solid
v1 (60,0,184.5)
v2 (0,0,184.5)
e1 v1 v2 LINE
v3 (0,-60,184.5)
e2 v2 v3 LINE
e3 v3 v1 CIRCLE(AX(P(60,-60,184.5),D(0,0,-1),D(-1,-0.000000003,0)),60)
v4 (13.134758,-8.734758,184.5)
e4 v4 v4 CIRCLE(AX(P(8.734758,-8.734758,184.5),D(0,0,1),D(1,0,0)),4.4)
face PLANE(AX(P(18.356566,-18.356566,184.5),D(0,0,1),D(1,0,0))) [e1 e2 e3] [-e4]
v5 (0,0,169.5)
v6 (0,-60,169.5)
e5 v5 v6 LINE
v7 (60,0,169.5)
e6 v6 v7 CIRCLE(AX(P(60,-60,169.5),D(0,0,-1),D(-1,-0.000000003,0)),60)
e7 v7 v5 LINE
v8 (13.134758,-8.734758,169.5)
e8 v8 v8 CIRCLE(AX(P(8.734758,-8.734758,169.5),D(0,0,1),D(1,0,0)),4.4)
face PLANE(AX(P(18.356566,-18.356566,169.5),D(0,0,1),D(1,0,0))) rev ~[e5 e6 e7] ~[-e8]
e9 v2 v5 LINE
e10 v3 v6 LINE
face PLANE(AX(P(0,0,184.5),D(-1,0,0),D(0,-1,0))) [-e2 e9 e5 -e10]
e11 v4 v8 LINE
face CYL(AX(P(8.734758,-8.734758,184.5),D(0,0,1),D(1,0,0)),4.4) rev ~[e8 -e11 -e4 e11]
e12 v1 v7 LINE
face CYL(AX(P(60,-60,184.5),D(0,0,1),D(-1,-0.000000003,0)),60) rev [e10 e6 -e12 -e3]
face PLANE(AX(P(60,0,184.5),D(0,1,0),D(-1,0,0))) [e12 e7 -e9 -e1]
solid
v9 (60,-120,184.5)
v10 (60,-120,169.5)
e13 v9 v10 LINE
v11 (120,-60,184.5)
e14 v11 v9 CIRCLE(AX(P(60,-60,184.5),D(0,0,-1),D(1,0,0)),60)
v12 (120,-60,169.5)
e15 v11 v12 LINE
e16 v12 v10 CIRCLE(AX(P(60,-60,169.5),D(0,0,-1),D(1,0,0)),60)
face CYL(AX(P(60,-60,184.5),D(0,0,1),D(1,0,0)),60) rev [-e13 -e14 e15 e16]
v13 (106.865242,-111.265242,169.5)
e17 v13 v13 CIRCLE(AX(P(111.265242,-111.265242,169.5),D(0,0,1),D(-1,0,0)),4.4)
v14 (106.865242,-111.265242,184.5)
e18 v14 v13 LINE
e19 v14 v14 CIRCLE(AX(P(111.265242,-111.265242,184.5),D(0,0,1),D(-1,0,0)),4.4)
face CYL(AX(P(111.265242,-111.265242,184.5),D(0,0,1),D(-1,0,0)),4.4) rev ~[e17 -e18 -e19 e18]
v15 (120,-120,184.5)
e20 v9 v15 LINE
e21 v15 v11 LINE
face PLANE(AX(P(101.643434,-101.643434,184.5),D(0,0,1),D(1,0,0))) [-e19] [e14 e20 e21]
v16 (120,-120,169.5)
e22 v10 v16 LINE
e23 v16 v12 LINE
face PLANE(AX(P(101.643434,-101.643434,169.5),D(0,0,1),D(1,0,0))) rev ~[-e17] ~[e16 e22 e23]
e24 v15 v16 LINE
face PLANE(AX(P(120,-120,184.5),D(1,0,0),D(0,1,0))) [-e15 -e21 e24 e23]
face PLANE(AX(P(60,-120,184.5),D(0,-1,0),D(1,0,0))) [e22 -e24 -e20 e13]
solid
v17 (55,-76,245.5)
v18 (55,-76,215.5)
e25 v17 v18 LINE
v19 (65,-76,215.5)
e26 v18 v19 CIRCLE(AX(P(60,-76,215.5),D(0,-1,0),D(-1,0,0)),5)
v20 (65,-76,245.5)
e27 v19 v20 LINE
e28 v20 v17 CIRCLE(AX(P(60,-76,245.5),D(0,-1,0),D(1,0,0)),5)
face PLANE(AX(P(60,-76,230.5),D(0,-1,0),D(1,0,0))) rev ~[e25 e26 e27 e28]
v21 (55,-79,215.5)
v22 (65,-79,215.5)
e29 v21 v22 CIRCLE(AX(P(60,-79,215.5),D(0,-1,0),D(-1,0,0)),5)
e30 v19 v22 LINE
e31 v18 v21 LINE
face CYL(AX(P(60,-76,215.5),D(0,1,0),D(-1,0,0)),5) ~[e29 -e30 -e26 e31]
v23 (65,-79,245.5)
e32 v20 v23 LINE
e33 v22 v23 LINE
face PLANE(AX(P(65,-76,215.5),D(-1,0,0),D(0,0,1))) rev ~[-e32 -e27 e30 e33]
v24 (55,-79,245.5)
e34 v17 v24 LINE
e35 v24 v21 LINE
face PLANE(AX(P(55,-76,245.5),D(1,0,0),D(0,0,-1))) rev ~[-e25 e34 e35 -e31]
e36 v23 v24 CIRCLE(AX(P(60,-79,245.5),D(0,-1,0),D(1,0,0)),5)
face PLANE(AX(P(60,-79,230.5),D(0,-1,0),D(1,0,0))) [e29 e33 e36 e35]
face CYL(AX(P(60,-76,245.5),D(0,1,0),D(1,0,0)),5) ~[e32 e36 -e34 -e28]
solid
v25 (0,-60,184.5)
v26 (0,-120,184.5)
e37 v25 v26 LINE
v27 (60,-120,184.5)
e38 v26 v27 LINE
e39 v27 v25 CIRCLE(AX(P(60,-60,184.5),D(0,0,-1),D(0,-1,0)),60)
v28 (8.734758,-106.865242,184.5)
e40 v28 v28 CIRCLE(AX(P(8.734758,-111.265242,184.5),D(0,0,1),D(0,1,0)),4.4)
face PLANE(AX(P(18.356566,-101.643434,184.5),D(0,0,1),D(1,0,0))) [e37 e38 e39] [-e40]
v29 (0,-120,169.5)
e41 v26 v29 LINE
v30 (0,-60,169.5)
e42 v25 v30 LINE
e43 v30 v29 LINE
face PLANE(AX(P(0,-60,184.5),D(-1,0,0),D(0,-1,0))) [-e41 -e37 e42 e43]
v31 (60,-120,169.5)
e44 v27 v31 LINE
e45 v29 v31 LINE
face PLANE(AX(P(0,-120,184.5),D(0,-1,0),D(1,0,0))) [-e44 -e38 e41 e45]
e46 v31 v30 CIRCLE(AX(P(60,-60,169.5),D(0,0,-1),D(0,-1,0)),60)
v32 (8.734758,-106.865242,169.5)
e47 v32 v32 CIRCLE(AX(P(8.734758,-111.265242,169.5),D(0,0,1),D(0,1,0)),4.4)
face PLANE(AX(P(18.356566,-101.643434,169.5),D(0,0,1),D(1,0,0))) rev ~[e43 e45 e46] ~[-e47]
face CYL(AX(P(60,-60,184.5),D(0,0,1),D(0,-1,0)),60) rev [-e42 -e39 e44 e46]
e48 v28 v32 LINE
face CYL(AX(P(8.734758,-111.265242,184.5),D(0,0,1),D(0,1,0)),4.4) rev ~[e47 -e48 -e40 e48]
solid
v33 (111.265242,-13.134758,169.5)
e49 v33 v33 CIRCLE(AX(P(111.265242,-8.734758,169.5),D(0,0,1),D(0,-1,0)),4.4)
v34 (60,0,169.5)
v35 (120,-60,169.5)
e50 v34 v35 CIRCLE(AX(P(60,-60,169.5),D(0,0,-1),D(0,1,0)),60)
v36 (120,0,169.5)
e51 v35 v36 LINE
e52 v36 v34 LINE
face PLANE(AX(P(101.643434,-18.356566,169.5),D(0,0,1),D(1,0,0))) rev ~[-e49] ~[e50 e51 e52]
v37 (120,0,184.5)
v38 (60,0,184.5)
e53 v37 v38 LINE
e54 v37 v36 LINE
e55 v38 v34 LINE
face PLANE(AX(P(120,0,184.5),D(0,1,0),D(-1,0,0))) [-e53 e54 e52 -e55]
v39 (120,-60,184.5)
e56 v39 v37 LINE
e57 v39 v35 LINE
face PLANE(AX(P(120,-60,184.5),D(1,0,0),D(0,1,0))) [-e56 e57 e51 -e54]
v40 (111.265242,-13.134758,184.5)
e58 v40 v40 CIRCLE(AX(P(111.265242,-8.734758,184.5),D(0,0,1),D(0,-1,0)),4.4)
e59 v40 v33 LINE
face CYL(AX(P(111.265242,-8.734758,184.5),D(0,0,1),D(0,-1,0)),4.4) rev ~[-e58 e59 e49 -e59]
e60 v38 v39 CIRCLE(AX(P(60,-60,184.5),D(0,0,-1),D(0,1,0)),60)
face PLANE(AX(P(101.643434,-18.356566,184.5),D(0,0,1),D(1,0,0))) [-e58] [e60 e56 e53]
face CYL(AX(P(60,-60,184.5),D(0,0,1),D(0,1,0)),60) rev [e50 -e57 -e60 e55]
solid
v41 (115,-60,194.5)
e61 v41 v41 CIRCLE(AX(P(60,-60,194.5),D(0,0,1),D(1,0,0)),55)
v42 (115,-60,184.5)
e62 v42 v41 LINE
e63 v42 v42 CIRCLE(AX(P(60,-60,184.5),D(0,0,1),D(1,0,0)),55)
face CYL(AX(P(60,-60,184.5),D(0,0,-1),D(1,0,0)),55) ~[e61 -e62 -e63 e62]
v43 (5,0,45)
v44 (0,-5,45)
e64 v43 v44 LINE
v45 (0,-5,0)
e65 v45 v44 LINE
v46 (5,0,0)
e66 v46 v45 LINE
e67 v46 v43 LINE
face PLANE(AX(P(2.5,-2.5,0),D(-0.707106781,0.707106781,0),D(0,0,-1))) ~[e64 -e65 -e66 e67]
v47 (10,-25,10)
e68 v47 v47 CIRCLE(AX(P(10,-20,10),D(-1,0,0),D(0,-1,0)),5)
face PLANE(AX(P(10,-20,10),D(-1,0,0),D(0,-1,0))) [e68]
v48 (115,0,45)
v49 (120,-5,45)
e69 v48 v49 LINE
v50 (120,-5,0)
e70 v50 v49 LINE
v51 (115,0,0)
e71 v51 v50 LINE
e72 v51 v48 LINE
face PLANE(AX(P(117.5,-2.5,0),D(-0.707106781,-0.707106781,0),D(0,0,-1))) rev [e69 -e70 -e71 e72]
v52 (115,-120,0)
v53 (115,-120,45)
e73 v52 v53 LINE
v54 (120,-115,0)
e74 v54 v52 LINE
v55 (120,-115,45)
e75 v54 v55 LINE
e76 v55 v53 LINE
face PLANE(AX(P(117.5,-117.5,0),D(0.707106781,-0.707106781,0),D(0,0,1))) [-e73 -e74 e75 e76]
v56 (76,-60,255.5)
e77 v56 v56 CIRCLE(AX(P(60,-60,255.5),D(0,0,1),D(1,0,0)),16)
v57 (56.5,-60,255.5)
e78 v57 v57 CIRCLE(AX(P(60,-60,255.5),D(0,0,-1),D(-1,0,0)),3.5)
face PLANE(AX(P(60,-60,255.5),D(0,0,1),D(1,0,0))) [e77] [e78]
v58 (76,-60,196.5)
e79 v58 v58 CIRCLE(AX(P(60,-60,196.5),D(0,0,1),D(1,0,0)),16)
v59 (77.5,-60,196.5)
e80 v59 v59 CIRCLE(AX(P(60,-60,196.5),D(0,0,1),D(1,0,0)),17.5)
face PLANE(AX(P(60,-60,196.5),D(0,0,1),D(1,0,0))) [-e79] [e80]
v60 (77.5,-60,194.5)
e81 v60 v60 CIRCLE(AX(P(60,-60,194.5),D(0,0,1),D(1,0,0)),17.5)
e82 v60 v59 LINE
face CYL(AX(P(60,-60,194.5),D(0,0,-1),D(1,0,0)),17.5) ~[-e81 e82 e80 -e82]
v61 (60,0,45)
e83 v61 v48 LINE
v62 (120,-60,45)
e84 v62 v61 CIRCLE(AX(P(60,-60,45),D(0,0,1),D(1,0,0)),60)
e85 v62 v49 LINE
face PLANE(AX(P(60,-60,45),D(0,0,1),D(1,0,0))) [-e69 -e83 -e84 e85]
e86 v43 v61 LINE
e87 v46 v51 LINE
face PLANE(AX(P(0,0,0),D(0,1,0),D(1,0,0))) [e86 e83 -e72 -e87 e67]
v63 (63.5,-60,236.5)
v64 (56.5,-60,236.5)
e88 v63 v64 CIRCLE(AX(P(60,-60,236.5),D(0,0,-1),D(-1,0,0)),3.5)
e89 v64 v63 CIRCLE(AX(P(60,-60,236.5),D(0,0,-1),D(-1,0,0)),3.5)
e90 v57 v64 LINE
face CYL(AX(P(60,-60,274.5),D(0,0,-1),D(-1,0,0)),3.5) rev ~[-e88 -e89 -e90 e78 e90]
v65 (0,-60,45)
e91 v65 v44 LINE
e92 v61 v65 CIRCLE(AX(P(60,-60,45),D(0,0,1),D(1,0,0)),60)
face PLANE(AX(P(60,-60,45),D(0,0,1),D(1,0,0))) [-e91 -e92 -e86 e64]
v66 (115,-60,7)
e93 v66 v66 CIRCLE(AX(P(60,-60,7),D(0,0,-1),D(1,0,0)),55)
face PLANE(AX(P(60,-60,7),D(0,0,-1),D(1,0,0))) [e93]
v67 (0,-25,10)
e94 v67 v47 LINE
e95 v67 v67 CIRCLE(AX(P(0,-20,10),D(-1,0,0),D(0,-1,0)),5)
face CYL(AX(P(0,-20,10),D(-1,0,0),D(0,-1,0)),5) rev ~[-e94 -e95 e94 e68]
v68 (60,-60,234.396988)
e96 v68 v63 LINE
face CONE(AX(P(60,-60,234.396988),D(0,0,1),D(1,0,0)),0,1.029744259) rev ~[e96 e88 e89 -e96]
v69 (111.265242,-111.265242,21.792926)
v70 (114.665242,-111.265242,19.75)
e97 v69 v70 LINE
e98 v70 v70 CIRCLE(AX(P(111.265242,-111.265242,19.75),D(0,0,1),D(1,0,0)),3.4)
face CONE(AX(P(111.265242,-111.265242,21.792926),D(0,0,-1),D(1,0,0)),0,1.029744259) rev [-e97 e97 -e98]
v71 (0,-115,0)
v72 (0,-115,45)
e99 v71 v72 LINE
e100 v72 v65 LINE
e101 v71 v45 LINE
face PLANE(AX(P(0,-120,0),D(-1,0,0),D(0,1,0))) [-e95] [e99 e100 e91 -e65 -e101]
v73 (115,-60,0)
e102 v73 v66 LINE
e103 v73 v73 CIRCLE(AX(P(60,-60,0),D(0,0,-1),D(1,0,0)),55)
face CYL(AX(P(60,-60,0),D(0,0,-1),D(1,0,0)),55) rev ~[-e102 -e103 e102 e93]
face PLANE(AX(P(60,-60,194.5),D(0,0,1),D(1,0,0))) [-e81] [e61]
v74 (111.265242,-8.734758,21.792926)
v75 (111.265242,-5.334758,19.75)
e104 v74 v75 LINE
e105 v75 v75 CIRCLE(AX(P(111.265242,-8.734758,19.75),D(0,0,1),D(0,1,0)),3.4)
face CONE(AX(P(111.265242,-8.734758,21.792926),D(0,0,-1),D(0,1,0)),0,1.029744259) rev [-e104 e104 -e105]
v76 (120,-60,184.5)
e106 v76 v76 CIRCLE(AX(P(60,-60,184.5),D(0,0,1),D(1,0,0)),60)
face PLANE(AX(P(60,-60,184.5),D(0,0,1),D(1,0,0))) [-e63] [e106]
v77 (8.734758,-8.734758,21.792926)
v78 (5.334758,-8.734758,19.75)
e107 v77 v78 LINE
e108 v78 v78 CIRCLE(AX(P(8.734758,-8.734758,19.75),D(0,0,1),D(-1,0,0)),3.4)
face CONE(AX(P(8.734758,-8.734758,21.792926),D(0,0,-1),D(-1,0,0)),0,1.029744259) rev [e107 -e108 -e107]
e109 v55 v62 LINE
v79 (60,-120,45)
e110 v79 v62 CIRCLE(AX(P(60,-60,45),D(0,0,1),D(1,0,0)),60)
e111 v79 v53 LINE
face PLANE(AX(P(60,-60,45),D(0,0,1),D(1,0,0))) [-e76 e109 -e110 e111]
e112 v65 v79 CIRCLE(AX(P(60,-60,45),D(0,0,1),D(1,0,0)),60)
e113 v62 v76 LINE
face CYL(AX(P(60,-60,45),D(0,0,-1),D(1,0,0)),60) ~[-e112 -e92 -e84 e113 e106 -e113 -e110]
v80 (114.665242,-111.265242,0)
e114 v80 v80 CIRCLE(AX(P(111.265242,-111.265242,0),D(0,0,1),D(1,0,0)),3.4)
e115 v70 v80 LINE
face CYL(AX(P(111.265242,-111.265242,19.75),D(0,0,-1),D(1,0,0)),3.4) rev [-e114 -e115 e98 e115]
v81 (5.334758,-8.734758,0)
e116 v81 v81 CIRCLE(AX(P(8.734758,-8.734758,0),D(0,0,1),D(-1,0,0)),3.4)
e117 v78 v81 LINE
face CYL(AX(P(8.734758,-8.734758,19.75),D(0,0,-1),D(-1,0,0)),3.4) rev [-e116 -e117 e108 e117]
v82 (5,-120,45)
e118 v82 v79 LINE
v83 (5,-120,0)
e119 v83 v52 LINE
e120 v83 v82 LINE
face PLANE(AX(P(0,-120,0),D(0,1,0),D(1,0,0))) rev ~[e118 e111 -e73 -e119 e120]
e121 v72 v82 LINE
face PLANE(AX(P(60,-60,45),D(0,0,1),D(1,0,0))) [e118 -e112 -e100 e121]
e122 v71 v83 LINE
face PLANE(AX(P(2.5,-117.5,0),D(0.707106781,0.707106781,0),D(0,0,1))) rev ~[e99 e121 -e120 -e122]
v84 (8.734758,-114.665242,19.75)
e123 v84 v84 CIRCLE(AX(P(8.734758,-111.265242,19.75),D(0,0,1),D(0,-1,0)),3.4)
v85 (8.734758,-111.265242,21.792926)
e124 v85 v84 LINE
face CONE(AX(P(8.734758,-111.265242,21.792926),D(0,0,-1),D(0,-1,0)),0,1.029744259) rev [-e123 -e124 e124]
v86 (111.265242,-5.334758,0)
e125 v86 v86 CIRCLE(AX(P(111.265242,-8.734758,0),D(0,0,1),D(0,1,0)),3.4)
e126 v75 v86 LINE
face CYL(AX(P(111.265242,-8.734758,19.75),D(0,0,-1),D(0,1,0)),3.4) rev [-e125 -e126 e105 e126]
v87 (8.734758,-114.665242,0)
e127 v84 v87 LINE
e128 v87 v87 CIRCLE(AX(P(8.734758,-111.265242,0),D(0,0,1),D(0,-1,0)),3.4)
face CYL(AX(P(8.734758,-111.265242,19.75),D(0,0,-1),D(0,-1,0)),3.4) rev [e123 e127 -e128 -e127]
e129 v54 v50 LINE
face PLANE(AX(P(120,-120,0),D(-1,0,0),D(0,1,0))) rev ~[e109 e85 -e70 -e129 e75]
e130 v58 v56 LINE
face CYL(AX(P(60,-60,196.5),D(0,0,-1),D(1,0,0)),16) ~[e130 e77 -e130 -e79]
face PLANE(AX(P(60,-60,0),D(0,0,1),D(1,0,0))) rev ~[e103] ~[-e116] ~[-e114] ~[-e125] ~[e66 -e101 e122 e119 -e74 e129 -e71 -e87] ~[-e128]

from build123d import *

# Parameters (mm, degrees)
SKETCH1_W                 = 120
SKETCH1_H                 = 120
EXTRUDE1_DEPTH            = 45
SKETCH2_R                 = 60
EXTRUDE2_DEPTH            = 139.5
SKETCH3_R                 = 55
EXTRUDE3_DEPTH            = 10
SKETCH4_R                 = 17.5
EXTRUDE4_DEPTH            = 2
SKETCH5_R                 = 16
EXTRUDE5_DEPTH            = 59
CHAMFER1_SIZE             = 5
M8X1_0_TAPPED_HOLE1_D     = 7
M8X1_0_TAPPED_HOLE1_DEPTH = 19
M8X1_0_TAPPED_HOLE1_TIP   = 2.103012167
EXTRUDE6_DEPTH            = 3
SKETCH19_R                = 5
CUT_EXTRUDE1_DEPTH        = 10
SKETCH20_R                = 55
CUT_EXTRUDE2_DEPTH        = 7
CIRPATTERN1_COUNT         = 4
BOSS_EXTRUDE1_DEPTH       = 15
BOSS_EXTRUDE1_2_DEPTH     = 15
BOSS_EXTRUDE1_3_DEPTH     = 15
BOSS_EXTRUDE1_4_DEPTH     = 15
SKETCH24_R                = 4.4
CUT_EXTRUDE3_DEPTH        = 15
CIRPATTERN2_COUNT         = 4


with BuildPart() as part:
    # Sketch1 → Extrude1 (new body)
    with BuildSketch(Plane.XY):
        with Locations((60, -60)):
            Rectangle(SKETCH1_W, SKETCH1_H)
    extrude(amount=EXTRUDE1_DEPTH)

    # Sketch2 → Extrude2 (add)
    with BuildSketch(Plane.XY.offset(45)):
        with Locations((60, -60)):
            Circle(SKETCH2_R)
    extrude(amount=EXTRUDE2_DEPTH)

    # Sketch3 → Extrude3 (add)
    with BuildSketch(Plane.XY.offset(184.5)):
        with Locations((60, -60)):
            Circle(SKETCH3_R)
    extrude(amount=EXTRUDE3_DEPTH)

    # Sketch4 → Extrude4 (add)
    with BuildSketch(Plane.XY.offset(194.5)):
        with Locations((60, -60)):
            Circle(SKETCH4_R)
    extrude(amount=EXTRUDE4_DEPTH)

    # Sketch5 → Extrude5 (add)
    with BuildSketch(Plane.XY.offset(196.5)):
        with Locations((60, -60)):
            Circle(SKETCH5_R)
    extrude(amount=EXTRUDE5_DEPTH)

    # Chamfer1
    chamfer1_edges = [part.edges().sort_by_distance(p)[0] for p in [
        (0, 0, 22.5),
        (120, 0, 22.5),
        (120, -120, 22.5),
        (0, -120, 22.5),
    ]]
    chamfer(chamfer1_edges, length=CHAMFER1_SIZE)

    # M8x1.0 Tapped Hole1
    with Locations(Plane.XY.offset(255.5)):
        with Locations((60, -60)):
            Hole(M8X1_0_TAPPED_HOLE1_D / 2, depth=M8X1_0_TAPPED_HOLE1_DEPTH)
            with Locations((0, 0, -(M8X1_0_TAPPED_HOLE1_DEPTH + M8X1_0_TAPPED_HOLE1_TIP / 2))):  # 118° drill point
                Cone(0, M8X1_0_TAPPED_HOLE1_D / 2, M8X1_0_TAPPED_HOLE1_TIP, mode=Mode.SUBTRACT)

    # Sketch19 → Cut-Extrude1 (cut)
    with BuildSketch(Plane.ZY):
        with Locations(Location((10, -20, 0), (0, 0, 270))):
            Circle(SKETCH19_R)
    extrude(amount=-CUT_EXTRUDE1_DEPTH, mode=Mode.SUBTRACT)

    # Sketch20 → Cut-Extrude2 (cut)
    with BuildSketch(Plane(origin=(0, 0, 0), x_dir=(-1, 0, 0), z_dir=(0, 0, -1))):
        with Locations(Location((-60, -60, 0), (0, 0, 180))):
            Circle(SKETCH20_R)
    extrude(amount=-CUT_EXTRUDE2_DEPTH, mode=Mode.SUBTRACT)

    # Sketch21 → M8 Tapped Hole1 (revolve, cut)
    with BuildSketch(Plane(origin=(111.265241636, -8.734758364, 0), x_dir=(0, 1, 0), z_dir=(1, 0, 0))):
        Polygon((0, 0), (0, 21.792926105), (3.4, 19.75), (3.4, 0), align=None)
    m8_tapped_hole1 = revolve(axis=Axis((111.265241636, -8.734758364, -6.35), (0, 0, 1)), mode=Mode.SUBTRACT)

    # CirPattern1: M8 Tapped Hole1 ×4 about axis
    cirpattern1_axis = Axis((60, -60, 0), (0, 0, 1))
    for i in range(1, CIRPATTERN1_COUNT):
        add(m8_tapped_hole1.rotate(cirpattern1_axis, i * 360 / CIRPATTERN1_COUNT), mode=Mode.SUBTRACT)


with BuildPart() as body_2:
    # Sketch18 → Extrude6 (new body)
    with BuildSketch(Plane.XZ.offset(76)):
        with BuildLine():
            Line((55, 245.5), (55, 215.5))
            ThreePointArc((55, 215.5), (60, 210.5), (65, 215.5))
            Line((65, 215.5), (65, 245.5))
            ThreePointArc((65, 245.5), (60, 250.5), (55, 245.5))
        make_face()
    extrude(amount=EXTRUDE6_DEPTH)


with BuildPart() as body_3:
    # Sketch23 → Boss-Extrude1 (new body)
    with BuildSketch(Plane.XY.offset(184.5)):
        with BuildLine():
            Line((120, 0), (60, 0))
            ThreePointArc((60, 0), (102.426406871, -17.573593129), (120, -60))
            Line((120, -60), (120, 0))
        make_face()
    extrude(amount=-BOSS_EXTRUDE1_DEPTH)


with BuildPart() as body_4:
    # Sketch23 → Boss-Extrude1 2 (new body)
    with BuildSketch(Plane.XY.offset(184.5)):
        with BuildLine():
            Line((60, 0), (0, 0))
            Line((0, 0), (0, -60.000000158))
            ThreePointArc((0, -60.000000158), (17.573593073, -17.573593185), (60, 0))
        make_face()
    extrude(amount=-BOSS_EXTRUDE1_2_DEPTH)

    # Sketch24 → Cut-Extrude3 (cut)
    with BuildSketch(Plane.XY.offset(184.5)):
        with Locations((8.734758364, -8.734758364)):
            Circle(SKETCH24_R)
    cut_extrude3 = extrude(amount=-CUT_EXTRUDE3_DEPTH, mode=Mode.SUBTRACT)


with BuildPart() as body_5:
    # Sketch23 → Boss-Extrude1 3 (new body)
    with BuildSketch(Plane.XY.offset(184.5)):
        with BuildLine():
            ThreePointArc((60, -120), (17.573593185, -102.426406927), (0, -60.000000158))
            Line((0, -60.000000158), (0, -120))
            Line((0, -120), (60, -120))
        make_face()
    extrude(amount=-BOSS_EXTRUDE1_3_DEPTH)


with BuildPart() as body_6:
    # Sketch23 → Boss-Extrude1 4 (new body)
    with BuildSketch(Plane.XY.offset(184.5)):
        with BuildLine():
            Line((120, -120), (120, -60))
            ThreePointArc((120, -60), (102.426406871, -102.426406871), (60, -120))
            Line((60, -120), (120, -120))
        make_face()
    extrude(amount=-BOSS_EXTRUDE1_4_DEPTH)


with BuildPart() as cirpattern2_tool:
    # CirPattern2: Cut-Extrude3 ×4 about axis
    cirpattern2_axis = Axis((60, -60, 0), (0, 0, 1))
    for i in range(1, CIRPATTERN2_COUNT):
        add(cut_extrude3.rotate(cirpattern2_axis, i * 360 / CIRPATTERN2_COUNT))


with BuildPart() as body_3_1:
    add(body_3.part)

    # CirPattern2: cut by cirpattern2_tool
    add(cirpattern2_tool.part, mode=Mode.SUBTRACT)


with BuildPart() as body_5_1:
    add(body_5.part)

    # CirPattern2: cut by cirpattern2_tool
    add(cirpattern2_tool.part, mode=Mode.SUBTRACT)


with BuildPart() as body_6_1:
    add(body_6.part)

    # CirPattern2: cut by cirpattern2_tool
    add(cirpattern2_tool.part, mode=Mode.SUBTRACT)


solid = Compound([part.part, body_2.part, body_4.part, body_3_1.part, body_5_1.part, body_6_1.part])
